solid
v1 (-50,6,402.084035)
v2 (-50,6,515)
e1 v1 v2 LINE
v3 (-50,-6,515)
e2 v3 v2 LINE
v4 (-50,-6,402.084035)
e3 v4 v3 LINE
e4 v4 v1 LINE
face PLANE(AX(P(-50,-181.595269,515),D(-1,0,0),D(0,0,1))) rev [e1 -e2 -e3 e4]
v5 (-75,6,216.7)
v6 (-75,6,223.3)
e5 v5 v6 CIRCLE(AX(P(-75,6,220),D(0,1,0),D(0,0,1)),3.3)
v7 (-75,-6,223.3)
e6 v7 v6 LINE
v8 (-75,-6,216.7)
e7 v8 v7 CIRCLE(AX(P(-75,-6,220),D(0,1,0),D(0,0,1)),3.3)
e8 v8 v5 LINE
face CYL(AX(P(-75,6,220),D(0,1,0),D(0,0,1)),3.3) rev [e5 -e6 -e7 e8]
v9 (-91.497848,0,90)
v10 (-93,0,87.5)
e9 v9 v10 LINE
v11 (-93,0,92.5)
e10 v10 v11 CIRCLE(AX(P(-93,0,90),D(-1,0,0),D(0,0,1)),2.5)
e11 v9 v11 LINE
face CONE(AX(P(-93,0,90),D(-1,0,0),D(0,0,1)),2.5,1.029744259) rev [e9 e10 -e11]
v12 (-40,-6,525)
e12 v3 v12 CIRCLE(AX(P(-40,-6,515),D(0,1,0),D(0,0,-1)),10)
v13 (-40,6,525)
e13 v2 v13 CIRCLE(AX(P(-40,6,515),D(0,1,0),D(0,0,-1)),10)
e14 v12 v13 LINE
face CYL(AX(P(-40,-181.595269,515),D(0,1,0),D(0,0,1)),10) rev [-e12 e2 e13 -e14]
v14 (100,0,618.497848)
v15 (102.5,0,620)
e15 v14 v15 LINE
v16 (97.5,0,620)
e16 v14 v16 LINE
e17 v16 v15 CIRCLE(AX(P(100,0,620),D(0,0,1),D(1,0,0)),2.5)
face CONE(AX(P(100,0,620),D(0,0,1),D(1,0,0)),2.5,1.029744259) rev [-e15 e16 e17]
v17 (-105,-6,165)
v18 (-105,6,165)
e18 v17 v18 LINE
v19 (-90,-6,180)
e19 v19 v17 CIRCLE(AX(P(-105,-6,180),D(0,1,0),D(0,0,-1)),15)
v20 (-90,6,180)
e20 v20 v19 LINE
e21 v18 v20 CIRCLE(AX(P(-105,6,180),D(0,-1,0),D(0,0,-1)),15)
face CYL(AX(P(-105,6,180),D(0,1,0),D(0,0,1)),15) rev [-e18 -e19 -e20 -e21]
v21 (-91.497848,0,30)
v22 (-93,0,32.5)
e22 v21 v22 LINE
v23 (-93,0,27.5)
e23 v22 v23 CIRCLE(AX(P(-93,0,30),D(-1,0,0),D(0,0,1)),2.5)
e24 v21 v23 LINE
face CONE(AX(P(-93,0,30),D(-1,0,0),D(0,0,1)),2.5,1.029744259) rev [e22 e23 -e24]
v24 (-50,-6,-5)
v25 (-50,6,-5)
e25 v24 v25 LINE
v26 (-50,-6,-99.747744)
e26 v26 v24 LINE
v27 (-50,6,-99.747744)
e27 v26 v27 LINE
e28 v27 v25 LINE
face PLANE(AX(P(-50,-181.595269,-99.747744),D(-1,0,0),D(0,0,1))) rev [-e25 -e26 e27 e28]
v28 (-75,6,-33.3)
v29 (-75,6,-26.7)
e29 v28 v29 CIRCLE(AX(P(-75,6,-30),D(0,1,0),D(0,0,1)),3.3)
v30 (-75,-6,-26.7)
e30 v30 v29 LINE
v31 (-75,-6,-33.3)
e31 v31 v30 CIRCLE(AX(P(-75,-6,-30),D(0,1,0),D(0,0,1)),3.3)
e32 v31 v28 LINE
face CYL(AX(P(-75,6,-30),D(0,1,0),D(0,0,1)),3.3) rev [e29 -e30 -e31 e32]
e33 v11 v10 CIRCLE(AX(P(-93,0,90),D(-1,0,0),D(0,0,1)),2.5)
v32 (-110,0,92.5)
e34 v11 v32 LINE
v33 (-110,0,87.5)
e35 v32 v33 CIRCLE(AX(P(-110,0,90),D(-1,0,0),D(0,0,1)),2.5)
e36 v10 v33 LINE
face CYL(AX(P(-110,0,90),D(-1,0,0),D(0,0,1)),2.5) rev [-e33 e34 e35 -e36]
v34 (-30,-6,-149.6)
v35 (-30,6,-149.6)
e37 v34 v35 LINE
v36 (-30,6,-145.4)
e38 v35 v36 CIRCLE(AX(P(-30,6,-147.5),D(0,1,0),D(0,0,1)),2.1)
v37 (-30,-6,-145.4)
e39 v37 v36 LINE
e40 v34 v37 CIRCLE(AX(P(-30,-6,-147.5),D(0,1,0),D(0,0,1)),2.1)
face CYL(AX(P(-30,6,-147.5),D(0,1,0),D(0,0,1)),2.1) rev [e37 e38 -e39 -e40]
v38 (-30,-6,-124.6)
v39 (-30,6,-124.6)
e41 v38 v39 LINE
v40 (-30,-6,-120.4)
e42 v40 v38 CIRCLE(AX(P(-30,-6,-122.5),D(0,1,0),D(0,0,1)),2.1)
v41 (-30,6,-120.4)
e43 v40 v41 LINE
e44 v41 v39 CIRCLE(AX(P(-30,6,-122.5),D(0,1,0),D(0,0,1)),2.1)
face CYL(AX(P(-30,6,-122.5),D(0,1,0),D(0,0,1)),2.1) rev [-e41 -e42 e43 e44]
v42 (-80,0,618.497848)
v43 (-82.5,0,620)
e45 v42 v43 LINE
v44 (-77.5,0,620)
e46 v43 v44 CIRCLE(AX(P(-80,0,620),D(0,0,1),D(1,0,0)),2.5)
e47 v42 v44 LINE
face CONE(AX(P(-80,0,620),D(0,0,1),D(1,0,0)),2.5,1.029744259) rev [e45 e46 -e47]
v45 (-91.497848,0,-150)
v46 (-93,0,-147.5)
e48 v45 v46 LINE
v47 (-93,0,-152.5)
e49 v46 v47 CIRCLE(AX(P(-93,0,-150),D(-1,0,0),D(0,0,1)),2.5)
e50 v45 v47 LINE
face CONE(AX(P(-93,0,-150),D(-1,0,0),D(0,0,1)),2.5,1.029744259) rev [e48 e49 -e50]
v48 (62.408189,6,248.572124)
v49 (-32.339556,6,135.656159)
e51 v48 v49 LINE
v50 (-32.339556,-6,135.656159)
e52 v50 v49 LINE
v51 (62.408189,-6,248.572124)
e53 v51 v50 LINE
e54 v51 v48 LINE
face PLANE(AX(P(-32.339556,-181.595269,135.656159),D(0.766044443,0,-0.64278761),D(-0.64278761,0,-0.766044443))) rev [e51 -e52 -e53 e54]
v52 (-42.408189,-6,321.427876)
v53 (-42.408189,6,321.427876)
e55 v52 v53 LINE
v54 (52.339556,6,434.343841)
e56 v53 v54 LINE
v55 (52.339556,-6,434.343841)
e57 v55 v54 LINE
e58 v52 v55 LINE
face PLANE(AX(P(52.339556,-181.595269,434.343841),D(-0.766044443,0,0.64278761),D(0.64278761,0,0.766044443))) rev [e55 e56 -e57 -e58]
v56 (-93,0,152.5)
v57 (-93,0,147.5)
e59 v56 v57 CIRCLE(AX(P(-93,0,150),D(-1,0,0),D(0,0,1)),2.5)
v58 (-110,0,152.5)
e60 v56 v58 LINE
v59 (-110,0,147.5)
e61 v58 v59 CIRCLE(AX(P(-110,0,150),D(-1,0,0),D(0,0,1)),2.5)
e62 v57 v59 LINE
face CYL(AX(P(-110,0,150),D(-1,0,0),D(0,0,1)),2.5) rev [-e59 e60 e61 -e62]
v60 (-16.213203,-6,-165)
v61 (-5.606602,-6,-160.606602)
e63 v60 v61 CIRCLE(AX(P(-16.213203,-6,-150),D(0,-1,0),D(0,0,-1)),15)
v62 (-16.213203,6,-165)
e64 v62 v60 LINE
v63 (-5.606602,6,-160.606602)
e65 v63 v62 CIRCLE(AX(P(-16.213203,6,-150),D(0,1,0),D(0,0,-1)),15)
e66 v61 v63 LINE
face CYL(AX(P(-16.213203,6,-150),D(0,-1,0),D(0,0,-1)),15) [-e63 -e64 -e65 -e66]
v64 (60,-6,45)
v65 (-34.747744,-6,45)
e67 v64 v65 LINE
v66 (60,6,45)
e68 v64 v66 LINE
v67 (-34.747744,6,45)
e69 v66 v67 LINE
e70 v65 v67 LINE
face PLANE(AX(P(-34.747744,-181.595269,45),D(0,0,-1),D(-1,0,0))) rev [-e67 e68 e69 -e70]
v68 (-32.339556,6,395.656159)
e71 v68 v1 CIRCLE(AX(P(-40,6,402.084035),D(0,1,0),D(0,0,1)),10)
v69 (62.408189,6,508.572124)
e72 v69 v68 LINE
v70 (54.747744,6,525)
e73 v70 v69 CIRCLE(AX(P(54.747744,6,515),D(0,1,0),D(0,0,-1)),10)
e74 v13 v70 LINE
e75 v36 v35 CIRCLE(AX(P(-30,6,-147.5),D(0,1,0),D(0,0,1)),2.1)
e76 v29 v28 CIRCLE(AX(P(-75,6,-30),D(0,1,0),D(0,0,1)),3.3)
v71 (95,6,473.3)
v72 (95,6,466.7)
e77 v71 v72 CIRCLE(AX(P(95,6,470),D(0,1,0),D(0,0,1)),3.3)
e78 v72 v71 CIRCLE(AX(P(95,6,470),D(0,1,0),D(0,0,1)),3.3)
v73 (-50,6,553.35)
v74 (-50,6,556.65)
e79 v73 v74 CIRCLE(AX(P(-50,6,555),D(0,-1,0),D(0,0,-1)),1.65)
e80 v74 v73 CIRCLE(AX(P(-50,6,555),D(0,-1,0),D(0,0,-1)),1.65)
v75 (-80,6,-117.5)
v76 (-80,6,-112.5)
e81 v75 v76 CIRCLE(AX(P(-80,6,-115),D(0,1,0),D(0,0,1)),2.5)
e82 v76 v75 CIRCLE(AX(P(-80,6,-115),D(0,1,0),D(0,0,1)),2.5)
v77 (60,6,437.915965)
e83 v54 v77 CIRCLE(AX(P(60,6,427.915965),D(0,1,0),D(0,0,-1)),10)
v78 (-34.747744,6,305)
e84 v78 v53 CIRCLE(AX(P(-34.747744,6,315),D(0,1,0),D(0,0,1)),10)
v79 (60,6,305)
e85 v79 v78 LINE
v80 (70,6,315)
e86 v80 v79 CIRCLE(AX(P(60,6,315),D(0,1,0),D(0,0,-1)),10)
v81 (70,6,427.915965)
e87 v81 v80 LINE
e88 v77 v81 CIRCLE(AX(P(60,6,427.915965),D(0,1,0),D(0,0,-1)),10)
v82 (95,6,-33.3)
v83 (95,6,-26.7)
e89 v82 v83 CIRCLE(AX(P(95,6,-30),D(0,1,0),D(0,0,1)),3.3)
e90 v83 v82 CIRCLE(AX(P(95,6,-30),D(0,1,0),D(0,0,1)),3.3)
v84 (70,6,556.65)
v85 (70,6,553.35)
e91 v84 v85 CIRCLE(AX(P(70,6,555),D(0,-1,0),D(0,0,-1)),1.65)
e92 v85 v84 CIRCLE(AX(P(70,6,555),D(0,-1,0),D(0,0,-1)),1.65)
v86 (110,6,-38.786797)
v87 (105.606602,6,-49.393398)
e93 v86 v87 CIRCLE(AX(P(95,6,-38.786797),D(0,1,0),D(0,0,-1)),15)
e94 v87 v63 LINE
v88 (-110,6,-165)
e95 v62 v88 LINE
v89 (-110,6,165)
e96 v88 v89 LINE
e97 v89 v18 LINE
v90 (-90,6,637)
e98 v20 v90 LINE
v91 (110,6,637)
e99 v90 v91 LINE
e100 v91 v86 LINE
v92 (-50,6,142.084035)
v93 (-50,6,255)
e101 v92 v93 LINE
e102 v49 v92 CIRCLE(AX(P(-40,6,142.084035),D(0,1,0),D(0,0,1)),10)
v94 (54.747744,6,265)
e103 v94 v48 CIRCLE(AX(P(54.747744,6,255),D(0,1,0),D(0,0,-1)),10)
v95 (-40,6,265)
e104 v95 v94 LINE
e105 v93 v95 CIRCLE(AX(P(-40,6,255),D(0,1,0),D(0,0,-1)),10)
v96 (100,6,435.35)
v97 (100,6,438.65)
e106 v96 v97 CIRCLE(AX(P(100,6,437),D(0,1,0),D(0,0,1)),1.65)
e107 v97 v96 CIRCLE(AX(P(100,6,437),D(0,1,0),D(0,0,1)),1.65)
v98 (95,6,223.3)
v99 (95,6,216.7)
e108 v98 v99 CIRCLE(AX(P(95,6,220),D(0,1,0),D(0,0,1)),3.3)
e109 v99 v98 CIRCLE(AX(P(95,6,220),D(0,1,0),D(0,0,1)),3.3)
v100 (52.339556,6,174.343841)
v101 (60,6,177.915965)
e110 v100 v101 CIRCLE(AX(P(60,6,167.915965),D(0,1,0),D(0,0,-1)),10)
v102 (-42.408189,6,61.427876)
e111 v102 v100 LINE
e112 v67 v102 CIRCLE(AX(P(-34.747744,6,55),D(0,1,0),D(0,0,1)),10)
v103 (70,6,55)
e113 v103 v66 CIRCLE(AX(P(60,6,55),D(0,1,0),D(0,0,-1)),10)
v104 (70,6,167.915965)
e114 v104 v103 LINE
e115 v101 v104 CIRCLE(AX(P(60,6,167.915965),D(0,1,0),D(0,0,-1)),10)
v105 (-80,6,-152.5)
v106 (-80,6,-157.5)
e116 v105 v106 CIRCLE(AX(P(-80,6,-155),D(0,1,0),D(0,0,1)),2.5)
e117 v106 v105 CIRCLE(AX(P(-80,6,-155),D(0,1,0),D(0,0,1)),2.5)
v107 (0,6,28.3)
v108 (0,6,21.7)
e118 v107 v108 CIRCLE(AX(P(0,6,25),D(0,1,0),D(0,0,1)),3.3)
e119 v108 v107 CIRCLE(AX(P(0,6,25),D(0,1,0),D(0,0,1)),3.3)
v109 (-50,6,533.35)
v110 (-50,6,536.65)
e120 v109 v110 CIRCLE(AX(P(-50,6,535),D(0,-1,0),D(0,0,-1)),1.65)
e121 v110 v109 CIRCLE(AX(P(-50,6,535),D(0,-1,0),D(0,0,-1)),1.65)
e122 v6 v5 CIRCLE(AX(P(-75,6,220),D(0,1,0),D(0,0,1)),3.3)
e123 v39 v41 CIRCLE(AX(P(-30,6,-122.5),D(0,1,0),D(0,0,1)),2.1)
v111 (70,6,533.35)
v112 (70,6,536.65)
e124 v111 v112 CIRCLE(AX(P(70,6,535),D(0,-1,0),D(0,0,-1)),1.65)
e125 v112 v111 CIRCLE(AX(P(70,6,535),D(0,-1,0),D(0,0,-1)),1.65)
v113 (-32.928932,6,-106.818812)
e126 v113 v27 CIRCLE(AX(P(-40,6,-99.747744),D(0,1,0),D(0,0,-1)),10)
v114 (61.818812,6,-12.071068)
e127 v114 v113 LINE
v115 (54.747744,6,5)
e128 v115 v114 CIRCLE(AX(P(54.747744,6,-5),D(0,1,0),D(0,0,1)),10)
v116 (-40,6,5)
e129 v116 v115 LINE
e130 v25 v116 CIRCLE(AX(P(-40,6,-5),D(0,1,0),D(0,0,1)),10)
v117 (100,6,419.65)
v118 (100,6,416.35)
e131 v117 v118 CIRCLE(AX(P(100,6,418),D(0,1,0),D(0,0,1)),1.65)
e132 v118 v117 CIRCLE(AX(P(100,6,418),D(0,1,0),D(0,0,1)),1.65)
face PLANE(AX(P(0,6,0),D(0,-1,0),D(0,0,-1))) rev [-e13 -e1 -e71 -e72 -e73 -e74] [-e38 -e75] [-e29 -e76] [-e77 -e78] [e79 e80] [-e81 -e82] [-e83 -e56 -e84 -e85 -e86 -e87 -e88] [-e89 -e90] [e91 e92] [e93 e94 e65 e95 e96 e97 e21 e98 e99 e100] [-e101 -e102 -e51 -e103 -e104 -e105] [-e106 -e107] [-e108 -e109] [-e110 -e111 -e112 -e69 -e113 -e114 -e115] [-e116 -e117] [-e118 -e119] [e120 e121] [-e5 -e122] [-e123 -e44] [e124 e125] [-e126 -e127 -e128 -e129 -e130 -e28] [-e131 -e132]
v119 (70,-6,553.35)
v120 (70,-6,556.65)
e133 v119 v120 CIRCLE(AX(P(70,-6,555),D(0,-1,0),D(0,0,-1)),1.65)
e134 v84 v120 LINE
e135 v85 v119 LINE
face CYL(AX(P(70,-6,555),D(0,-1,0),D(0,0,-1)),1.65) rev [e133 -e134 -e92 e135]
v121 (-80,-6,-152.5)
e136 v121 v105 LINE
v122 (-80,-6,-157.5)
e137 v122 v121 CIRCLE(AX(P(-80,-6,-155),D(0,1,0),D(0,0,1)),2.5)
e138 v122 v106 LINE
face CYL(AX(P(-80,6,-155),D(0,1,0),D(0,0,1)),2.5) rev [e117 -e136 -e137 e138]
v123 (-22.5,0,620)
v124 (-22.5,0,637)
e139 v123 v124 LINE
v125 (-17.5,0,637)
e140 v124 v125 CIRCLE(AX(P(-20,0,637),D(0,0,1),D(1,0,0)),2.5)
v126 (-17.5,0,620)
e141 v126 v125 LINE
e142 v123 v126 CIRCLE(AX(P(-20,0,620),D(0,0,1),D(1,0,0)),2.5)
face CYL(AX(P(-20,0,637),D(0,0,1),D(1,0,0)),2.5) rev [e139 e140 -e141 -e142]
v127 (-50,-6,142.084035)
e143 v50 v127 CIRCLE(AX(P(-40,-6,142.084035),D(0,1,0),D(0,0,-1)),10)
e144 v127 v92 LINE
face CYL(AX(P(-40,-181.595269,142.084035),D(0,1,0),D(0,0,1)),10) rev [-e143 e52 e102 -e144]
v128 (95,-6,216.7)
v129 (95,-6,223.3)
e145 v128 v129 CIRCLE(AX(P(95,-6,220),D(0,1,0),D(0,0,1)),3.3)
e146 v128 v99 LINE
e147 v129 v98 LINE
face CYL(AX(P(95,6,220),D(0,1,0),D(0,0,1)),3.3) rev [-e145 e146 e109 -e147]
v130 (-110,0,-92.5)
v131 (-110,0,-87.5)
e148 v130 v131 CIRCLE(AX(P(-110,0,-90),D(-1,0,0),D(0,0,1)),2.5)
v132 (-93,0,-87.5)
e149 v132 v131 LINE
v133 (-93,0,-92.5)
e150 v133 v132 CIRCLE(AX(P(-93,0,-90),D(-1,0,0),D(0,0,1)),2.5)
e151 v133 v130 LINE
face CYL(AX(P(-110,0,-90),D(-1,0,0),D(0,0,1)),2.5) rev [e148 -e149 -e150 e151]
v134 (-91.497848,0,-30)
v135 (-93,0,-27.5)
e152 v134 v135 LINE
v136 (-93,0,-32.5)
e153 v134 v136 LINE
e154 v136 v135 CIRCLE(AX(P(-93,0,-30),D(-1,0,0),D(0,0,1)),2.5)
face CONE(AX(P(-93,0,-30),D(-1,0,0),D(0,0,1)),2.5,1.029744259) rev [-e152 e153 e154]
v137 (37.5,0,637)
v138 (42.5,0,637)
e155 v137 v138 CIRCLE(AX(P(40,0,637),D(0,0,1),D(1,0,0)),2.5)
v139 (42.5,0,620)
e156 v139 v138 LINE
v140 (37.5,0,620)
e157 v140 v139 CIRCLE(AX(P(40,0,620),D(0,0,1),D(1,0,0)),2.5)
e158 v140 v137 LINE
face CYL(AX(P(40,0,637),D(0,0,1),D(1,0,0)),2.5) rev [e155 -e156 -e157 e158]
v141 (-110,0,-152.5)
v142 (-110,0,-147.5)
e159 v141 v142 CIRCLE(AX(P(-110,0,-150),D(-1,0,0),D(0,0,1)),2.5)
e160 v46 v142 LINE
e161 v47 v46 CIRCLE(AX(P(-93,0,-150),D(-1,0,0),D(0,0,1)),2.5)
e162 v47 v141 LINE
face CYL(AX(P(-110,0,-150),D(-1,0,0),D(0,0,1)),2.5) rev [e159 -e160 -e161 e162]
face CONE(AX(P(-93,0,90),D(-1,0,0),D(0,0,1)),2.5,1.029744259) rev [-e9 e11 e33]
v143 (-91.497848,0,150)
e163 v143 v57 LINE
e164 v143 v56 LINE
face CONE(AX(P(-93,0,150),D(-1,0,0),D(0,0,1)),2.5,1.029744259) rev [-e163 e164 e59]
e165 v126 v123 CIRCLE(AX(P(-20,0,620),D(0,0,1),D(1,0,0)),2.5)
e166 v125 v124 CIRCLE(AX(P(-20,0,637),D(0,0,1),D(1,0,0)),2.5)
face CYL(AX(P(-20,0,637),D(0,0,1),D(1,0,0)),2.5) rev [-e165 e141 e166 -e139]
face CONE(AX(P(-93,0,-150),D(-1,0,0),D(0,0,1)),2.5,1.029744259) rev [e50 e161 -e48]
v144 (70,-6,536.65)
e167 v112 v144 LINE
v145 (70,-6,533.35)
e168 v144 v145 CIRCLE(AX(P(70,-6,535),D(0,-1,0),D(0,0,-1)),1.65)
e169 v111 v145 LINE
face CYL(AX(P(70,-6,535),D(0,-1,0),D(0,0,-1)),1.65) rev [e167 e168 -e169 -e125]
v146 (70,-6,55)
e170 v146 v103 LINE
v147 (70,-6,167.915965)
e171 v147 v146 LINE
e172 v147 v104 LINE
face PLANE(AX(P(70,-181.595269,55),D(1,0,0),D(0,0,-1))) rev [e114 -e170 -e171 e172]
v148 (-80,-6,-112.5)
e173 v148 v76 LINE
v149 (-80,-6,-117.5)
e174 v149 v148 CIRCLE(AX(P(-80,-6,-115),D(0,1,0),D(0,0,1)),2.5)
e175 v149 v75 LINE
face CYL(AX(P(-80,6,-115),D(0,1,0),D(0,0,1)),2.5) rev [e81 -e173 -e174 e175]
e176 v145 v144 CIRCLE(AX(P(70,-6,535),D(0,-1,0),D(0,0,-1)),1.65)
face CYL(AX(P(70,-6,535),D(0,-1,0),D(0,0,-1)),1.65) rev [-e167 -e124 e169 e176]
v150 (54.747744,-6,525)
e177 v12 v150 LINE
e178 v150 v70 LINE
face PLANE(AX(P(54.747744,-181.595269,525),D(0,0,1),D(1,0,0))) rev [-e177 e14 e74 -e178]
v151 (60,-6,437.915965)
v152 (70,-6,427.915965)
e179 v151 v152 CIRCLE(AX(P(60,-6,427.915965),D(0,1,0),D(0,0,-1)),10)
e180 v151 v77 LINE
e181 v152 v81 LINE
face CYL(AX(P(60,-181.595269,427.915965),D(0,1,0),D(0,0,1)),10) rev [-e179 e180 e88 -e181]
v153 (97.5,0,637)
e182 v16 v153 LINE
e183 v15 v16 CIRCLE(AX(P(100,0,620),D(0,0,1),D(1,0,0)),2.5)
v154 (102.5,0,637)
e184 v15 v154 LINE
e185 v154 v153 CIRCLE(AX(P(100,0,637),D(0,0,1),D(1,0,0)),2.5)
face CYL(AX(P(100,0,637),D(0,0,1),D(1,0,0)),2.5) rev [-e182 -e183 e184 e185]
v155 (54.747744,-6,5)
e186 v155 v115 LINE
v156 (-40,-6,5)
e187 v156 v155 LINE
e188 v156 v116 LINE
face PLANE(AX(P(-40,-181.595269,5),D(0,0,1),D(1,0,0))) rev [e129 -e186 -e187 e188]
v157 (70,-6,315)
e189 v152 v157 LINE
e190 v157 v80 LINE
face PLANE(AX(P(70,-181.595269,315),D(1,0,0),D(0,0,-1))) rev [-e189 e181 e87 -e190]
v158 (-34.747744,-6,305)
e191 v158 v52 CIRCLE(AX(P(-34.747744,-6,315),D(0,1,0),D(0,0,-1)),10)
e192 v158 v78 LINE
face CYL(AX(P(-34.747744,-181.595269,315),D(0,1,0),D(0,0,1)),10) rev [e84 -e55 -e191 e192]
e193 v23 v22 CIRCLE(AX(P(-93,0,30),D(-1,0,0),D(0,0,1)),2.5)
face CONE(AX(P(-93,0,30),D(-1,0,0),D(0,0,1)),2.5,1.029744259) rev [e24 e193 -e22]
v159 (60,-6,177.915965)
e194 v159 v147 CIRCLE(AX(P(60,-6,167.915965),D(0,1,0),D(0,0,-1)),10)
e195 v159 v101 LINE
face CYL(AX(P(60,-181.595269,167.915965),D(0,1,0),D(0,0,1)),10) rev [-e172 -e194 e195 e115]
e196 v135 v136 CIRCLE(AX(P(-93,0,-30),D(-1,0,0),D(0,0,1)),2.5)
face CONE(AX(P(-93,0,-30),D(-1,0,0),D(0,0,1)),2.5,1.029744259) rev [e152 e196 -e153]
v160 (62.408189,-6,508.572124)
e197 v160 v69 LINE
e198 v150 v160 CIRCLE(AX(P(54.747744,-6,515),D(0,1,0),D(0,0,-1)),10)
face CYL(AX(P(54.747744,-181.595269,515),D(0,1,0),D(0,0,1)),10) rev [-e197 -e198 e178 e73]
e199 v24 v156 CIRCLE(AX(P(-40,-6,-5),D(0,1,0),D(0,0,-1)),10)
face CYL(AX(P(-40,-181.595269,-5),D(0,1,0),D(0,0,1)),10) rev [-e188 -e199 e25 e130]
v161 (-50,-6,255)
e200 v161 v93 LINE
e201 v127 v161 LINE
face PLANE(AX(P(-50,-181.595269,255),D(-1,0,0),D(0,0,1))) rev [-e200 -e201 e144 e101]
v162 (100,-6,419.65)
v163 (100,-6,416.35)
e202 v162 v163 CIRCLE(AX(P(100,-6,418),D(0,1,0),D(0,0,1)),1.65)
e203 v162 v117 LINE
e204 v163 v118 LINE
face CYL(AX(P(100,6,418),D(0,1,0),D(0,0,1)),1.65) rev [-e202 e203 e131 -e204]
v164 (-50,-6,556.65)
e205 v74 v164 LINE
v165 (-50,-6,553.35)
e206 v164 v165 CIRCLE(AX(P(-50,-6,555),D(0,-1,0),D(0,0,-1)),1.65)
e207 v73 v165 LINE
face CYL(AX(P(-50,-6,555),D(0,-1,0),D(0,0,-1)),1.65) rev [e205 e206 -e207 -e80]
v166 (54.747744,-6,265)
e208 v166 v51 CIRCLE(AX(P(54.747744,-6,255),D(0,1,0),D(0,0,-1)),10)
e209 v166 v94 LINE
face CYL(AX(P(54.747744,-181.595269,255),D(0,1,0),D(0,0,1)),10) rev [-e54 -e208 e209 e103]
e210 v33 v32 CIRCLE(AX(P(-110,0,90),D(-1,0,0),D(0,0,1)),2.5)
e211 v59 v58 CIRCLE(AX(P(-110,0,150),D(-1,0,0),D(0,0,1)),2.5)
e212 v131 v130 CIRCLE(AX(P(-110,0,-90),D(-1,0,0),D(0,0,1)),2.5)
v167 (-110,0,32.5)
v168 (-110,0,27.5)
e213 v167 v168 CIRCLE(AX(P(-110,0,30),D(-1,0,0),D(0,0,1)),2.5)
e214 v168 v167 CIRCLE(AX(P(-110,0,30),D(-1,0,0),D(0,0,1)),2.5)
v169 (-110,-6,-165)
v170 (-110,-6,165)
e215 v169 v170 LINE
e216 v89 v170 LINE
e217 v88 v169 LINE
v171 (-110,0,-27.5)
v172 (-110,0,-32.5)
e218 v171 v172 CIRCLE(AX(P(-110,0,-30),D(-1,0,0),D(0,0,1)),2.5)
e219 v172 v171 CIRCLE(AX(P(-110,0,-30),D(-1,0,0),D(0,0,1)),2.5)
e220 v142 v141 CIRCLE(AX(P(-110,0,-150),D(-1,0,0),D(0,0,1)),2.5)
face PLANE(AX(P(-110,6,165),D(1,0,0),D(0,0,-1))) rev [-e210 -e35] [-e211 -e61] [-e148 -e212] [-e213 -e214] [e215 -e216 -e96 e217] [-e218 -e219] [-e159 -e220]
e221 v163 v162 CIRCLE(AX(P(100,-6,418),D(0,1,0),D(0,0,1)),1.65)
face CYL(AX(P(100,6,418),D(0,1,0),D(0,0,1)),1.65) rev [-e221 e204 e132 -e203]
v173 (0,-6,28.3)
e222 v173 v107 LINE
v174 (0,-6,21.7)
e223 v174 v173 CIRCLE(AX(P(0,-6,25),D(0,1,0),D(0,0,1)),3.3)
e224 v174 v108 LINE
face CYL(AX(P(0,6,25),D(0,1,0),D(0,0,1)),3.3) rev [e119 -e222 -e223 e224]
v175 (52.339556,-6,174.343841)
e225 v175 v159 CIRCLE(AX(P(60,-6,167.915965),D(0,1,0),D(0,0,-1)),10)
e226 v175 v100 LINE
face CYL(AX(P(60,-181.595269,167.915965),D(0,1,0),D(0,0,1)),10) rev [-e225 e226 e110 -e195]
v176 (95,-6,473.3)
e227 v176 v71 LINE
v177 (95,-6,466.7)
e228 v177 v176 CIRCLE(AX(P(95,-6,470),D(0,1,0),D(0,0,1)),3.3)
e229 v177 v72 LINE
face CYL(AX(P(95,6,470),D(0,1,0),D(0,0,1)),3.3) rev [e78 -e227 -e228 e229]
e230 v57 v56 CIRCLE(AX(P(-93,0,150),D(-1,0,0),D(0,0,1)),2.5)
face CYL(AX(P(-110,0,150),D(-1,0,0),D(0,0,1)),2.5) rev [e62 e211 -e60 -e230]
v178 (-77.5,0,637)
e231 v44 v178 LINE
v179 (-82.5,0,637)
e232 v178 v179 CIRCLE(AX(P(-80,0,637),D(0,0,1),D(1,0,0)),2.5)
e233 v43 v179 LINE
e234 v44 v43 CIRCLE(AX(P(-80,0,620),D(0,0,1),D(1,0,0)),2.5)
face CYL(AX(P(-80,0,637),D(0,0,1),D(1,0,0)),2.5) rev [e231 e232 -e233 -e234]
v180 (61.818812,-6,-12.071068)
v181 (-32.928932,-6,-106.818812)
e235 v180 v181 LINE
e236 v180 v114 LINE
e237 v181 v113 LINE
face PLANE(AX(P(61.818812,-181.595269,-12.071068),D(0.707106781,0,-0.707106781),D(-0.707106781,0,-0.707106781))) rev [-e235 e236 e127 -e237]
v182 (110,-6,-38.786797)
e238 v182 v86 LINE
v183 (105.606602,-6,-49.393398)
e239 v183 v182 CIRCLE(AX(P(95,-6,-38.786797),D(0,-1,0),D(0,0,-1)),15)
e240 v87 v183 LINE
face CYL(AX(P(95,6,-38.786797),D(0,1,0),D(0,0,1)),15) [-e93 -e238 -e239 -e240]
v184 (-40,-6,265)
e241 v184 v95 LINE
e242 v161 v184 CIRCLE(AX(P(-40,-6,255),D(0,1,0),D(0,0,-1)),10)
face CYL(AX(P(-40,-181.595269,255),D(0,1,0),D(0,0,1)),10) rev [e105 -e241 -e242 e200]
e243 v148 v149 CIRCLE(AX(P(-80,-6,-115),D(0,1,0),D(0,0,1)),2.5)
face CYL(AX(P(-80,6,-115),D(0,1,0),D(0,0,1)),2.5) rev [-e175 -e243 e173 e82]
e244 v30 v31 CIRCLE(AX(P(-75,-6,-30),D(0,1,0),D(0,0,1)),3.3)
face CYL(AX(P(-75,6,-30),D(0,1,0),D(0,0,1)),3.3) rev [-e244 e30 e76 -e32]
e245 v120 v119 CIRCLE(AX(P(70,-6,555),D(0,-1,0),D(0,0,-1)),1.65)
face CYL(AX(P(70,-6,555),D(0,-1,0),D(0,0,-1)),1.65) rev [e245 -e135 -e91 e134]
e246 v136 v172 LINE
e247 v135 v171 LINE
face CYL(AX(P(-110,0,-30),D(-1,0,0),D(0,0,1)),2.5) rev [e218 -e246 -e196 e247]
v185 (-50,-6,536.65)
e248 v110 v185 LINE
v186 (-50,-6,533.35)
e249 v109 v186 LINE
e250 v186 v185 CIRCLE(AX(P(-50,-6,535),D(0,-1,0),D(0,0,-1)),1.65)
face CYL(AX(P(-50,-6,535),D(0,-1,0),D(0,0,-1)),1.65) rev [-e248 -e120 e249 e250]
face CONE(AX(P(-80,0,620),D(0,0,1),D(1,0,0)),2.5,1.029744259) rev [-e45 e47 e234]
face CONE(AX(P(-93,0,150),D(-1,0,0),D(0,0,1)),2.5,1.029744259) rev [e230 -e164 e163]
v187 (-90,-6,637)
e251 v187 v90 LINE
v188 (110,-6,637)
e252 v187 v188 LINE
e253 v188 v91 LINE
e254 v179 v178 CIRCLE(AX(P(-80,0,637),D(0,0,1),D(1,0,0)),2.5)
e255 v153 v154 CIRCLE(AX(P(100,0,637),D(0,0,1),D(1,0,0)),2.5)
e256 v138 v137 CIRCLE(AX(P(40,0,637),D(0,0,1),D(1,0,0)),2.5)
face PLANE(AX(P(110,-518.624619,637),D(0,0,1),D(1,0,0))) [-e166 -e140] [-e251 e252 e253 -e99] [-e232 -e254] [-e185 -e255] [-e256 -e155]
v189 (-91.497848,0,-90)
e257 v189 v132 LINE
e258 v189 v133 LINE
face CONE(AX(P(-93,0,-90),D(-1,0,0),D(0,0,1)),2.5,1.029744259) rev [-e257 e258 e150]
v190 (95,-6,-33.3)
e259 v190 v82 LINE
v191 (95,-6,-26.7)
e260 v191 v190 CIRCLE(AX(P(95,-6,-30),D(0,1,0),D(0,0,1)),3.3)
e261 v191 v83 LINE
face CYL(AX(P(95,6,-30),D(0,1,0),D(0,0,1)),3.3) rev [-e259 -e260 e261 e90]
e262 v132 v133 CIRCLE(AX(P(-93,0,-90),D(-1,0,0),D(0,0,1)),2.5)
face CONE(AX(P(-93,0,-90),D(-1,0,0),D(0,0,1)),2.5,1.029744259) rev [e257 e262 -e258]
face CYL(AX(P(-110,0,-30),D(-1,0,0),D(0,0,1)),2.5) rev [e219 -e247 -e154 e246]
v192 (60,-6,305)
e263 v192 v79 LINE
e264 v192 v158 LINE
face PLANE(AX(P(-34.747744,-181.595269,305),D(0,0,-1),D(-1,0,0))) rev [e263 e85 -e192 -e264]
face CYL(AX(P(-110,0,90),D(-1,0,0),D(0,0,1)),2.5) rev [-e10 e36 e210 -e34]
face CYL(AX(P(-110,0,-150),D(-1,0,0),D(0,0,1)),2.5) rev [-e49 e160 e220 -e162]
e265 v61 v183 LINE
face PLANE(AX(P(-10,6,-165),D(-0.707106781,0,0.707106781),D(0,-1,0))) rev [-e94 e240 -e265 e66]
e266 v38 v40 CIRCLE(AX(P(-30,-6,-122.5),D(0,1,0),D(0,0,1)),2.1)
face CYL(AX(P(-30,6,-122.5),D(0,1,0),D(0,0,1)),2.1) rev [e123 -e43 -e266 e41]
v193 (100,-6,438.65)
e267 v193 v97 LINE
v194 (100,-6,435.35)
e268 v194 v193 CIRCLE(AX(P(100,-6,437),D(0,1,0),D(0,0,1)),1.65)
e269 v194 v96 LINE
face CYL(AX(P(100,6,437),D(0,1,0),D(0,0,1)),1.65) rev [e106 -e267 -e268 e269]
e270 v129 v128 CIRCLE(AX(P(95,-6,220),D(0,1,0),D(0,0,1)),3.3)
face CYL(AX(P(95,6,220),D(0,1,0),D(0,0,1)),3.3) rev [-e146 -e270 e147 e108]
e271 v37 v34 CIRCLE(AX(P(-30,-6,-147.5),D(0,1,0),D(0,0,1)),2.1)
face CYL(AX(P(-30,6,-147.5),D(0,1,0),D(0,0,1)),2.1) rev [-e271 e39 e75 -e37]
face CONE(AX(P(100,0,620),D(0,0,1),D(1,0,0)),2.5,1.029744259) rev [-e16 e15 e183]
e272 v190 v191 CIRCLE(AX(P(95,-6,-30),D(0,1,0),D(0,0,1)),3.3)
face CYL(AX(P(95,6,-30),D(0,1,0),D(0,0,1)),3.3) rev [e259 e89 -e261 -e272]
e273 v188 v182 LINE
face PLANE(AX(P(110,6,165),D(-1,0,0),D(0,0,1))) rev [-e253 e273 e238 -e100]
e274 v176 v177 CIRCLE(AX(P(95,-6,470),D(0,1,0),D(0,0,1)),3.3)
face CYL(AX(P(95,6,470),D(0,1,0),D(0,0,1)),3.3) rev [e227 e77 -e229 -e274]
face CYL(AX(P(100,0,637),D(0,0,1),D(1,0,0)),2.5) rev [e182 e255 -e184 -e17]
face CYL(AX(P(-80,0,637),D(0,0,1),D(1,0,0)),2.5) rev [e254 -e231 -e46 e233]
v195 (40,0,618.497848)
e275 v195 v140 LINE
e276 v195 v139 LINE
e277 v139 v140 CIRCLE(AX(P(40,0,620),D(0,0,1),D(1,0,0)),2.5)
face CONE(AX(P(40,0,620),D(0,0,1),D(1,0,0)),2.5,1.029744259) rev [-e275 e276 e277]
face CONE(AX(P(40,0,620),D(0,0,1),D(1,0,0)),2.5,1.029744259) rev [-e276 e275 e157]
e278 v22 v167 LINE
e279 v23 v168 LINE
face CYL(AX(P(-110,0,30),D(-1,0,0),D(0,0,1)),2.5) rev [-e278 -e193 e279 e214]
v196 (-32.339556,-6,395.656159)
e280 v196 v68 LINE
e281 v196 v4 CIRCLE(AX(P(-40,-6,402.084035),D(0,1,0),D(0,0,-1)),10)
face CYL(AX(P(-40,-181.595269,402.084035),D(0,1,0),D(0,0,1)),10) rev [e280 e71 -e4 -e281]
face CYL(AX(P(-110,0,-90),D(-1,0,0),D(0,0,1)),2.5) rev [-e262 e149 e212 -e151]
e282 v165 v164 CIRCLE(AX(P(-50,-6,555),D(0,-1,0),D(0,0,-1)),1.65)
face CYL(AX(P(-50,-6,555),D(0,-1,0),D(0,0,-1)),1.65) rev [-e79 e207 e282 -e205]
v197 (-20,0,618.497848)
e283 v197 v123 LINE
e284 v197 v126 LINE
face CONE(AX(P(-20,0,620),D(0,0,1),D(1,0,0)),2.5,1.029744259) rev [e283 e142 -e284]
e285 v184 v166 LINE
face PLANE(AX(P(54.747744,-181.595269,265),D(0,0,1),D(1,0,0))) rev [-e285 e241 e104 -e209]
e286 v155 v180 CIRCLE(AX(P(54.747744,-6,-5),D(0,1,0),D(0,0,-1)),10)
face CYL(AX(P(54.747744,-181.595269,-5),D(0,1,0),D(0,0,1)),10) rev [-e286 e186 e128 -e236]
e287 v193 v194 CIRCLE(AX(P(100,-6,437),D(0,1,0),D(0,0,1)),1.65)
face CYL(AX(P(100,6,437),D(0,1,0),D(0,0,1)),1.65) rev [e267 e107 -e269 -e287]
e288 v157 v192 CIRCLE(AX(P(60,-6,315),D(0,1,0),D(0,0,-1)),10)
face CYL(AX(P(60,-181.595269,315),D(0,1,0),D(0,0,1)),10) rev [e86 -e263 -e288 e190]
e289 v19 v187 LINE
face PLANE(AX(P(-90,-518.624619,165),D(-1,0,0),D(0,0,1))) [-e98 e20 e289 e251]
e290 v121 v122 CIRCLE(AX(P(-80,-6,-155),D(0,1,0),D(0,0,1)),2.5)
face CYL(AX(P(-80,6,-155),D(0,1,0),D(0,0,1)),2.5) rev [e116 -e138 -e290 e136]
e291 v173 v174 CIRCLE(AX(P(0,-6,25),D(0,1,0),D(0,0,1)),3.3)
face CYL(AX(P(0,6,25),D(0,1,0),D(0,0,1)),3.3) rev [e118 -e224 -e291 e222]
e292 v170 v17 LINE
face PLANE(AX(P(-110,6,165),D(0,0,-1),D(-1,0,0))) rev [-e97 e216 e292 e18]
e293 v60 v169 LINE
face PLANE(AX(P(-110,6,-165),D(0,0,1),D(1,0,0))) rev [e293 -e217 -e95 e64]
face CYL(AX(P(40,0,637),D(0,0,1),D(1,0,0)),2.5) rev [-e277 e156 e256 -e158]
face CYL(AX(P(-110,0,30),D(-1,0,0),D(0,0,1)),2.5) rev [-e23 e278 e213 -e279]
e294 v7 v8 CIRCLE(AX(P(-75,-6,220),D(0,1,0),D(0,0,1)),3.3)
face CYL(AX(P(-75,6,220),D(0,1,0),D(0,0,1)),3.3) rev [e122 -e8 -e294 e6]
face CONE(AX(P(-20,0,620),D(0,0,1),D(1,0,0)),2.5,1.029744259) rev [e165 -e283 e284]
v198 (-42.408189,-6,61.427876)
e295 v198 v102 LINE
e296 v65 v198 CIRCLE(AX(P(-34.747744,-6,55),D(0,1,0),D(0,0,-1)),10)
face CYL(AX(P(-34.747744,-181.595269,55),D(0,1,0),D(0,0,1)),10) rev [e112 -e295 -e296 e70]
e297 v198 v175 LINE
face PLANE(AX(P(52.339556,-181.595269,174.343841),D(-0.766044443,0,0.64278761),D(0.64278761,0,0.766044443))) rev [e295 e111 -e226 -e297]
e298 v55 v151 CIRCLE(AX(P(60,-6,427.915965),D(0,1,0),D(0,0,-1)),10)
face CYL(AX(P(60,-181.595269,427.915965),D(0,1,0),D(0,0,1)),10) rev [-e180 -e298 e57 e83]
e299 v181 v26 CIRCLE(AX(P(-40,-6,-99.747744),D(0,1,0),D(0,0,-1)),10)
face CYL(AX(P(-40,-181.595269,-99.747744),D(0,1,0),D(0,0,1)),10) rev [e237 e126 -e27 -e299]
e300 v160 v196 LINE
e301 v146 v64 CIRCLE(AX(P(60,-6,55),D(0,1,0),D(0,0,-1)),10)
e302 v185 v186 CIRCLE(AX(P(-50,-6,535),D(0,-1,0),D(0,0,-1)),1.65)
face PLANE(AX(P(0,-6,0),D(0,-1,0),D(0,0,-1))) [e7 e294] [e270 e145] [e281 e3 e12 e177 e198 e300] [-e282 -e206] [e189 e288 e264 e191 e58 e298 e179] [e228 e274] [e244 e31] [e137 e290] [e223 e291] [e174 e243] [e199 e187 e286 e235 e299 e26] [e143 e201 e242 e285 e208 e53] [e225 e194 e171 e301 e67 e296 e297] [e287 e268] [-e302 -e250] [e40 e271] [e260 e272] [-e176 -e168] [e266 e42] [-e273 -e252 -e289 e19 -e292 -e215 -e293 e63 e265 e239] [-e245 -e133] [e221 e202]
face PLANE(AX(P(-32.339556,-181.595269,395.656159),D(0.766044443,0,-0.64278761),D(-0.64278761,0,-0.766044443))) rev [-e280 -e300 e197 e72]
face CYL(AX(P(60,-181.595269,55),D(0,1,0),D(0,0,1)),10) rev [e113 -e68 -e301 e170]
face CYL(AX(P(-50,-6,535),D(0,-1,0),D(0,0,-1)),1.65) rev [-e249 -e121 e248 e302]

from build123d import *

# Parameters (mm, degrees)
SKETCH_1_W             = 220
SKETCH_1_H             = 330
EXTRUDE_1_DEPTH        = 6
SKETCH_2_W             = 200
SKETCH_2_H             = 472
EXTRUDE_2_DEPTH        = 12
CHAMFER_1_SIZE         = 120
FILLET_2_R             = 15
CUT_EXTRUDE_3_DEPTH    = 12
HOLE_WIZARD_M6_1_D     = 5
HOLE_WIZARD_M6_1_DEPTH = 17
HOLE_WIZARD_M6_1_TIP   = 1.502151548
HOLE_WIZARD_M6_2_D     = 5
HOLE_WIZARD_M6_2_DEPTH = 17
HOLE_WIZARD_M6_2_TIP   = 1.502151548
HOLE_WIZARD_M6_1_2_D   = 6.6
HOLE_WIZARD_M6_2_2_D   = 6.6
HOLE_WIZARD_M6_3_D     = 5
HOLE_WIZARD_M5_1_D     = 4.2
HOLE_WIZARD_M4_1_D     = 3.3
HOLE_WIZARD_M4_2_D     = 3.3


with BuildPart() as part:
    # 草图1 → 凸台-拉伸1 (new, symmetric)
    with BuildSketch(Plane(origin=(0, 0, 0), x_dir=(1, 0, 0), z_dir=(0, 1, 0))):
        Rectangle(SKETCH_1_W, SKETCH_1_H)
    extrude(amount=EXTRUDE_1_DEPTH, both=True)

    # 草图2 → 凸台-拉伸2 (add)
    with BuildSketch(Plane(origin=(0, 6, 0), x_dir=(1, 0, 0), z_dir=(0, 1, 0))):
        with Locations((10, -401)):
            Rectangle(SKETCH_2_W, SKETCH_2_H)
    extrude(amount=-EXTRUDE_2_DEPTH)

    # 倒角1
    chamfer_1_edges = [part.edges().sort_by_distance(p)[0] for p in [
        (110, 0, -165),
    ]]
    chamfer(chamfer_1_edges, length=CHAMFER_1_SIZE)

    # 圆角2
    fillet_2_edges = [part.edges().sort_by_distance(p)[0] for p in [
        (-10, 0, -165),
        (110, 0, -45),
        (-90, 0, 165),
    ]]
    fillet(fillet_2_edges, radius=FILLET_2_R)

    # 草图7 → 切除-拉伸3 (cut)
    with BuildSketch(Plane(origin=(0, 6, 0), x_dir=(1, 0, 0), z_dir=(0, 1, 0))):
        with BuildLine():
            Line((-34.747744438, -45), (60, -45))
            ThreePointArc((60, -45), (67.071067812, -47.928932188), (70, -55))
            Line((70, -55), (70, -167.915964824))
            ThreePointArc((70, -167.915964824), (63.420201433, -177.312891032), (52.339555569, -174.343840921))
            Line((52.339555569, -174.343840921), (-42.408188869, -61.427876097))
            ThreePointArc((-42.408188869, -61.427876097), (-43.810822308, -50.773817383), (-34.747744438, -45))
        make_face()
        with BuildLine():
            Line((-32.339555569, -135.656159079), (62.408188869, -248.572123903))
            ThreePointArc((62.408188869, -248.572123903), (63.810822308, -259.226182617), (54.747744438, -265))
            Line((54.747744438, -265), (-40, -265))
            ThreePointArc((-40, -265), (-47.071067812, -262.071067812), (-50, -255))
            Line((-50, -255), (-50, -142.084035176))
            ThreePointArc((-50, -142.084035176), (-43.420201433, -132.687108968), (-32.339555569, -135.656159079))
        make_face()
        with BuildLine():
            Line((-34.747744438, -305), (60, -305))
            ThreePointArc((60, -305), (67.071067812, -307.928932188), (70, -315))
            Line((70, -315), (70, -427.915964824))
            ThreePointArc((70, -427.915964824), (63.420201433, -437.312891032), (52.339555569, -434.343840921))
            Line((52.339555569, -434.343840921), (-42.408188869, -321.427876097))
            ThreePointArc((-42.408188869, -321.427876097), (-43.810822308, -310.773817383), (-34.747744438, -305))
        make_face()
        with BuildLine():
            Line((-32.339555569, -395.656159079), (62.408188869, -508.572123903))
            ThreePointArc((62.408188869, -508.572123903), (63.810822308, -519.226182617), (54.747744438, -525))
            Line((54.747744438, -525), (-40, -525))
            ThreePointArc((-40, -525), (-47.071067812, -522.071067812), (-50, -515))
            Line((-50, -515), (-50, -402.084035176))
            ThreePointArc((-50, -402.084035176), (-43.420201433, -392.687108968), (-32.339555569, -395.656159079))
        make_face()
        with BuildLine():
            Line((-50, 99.747744438), (-50, 5))
            ThreePointArc((-50, 5), (-47.071067812, -2.071067812), (-40, -5))
            Line((-40, -5), (54.747744438, -5))
            ThreePointArc((54.747744438, -5), (63.986539763, 1.173165676), (61.81881225, 12.071067812))
            Line((61.81881225, 12.071067812), (-32.928932188, 106.81881225))
            ThreePointArc((-32.928932188, 106.81881225), (-43.826834324, 108.986539763), (-50, 99.747744438))
        make_face()
    extrude(amount=-CUT_EXTRUDE_3_DEPTH, mode=Mode.SUBTRACT)

    # Hole Wizard M6 _1
    with Locations(Plane.XY.offset(637)):
        with Locations((-80, 0), (-20, 0), (40, 0), (100, 0)):
            Hole(HOLE_WIZARD_M6_1_D / 2, depth=HOLE_WIZARD_M6_1_DEPTH)
            with Locations((0, 0, -(HOLE_WIZARD_M6_1_DEPTH + HOLE_WIZARD_M6_1_TIP / 2))):  # 118° drill point
                Cone(0, HOLE_WIZARD_M6_1_D / 2, HOLE_WIZARD_M6_1_TIP, mode=Mode.SUBTRACT)

    # Hole Wizard M6 _2
    with Locations(Plane.ZY.offset(110)):
        with Locations((-150, 0), (-90, 0), (-30, 0), (30, 0), (90, 0), (150, 0)):
            Hole(HOLE_WIZARD_M6_2_D / 2, depth=HOLE_WIZARD_M6_2_DEPTH)
            with Locations((0, 0, -(HOLE_WIZARD_M6_2_DEPTH + HOLE_WIZARD_M6_2_TIP / 2))):  # 118° drill point
                Cone(0, HOLE_WIZARD_M6_2_D / 2, HOLE_WIZARD_M6_2_TIP, mode=Mode.SUBTRACT)

    # Hole Wizard M6 _1 2 (through all)
    with Locations(Plane(origin=(0, 6, 0), x_dir=(1, 0, 0), z_dir=(0, 1, 0))):
        with Locations((95, 30), (-75, 30), (-75, -220), (95, -220), (95, -470)):
            Hole(HOLE_WIZARD_M6_1_2_D / 2)

    # Hole Wizard M6 _2 2 (through all)
    with Locations(Plane(origin=(0, 6, 0), x_dir=(1, 0, 0), z_dir=(0, 1, 0))):
        with Locations((0, -25)):
            Hole(HOLE_WIZARD_M6_2_2_D / 2)

    # M6 螺纹孔3 (through all)
    with Locations(Plane(origin=(0, 6, 0), x_dir=(1, 0, 0), z_dir=(0, 1, 0))):
        with Locations((-80, 155), (-80, 115)):
            Hole(HOLE_WIZARD_M6_3_D / 2)

    # M5 螺纹孔1 (through all)
    with Locations(Plane(origin=(0, 6, 0), x_dir=(1, 0, 0), z_dir=(0, 1, 0))):
        with Locations((-30, 147.5), (-30, 122.5)):
            Hole(HOLE_WIZARD_M5_1_D / 2)

    # M4 螺纹孔1 (through all)
    with Locations(Plane(origin=(0, 6, 0), x_dir=(1, 0, 0), z_dir=(0, 1, 0))):
        with Locations((100, -418), (100, -437)):
            Hole(HOLE_WIZARD_M4_1_D / 2)

    # M4 螺纹孔2 (through all)
    with Locations(Plane(origin=(0, -6, 0), x_dir=(-1, 0, 0), z_dir=(0, -1, 0))):
        with Locations((-70, -535), (50, -555), (-70, -555), (50, -535)):
            Hole(HOLE_WIZARD_M4_2_D / 2)


solid = part.part
